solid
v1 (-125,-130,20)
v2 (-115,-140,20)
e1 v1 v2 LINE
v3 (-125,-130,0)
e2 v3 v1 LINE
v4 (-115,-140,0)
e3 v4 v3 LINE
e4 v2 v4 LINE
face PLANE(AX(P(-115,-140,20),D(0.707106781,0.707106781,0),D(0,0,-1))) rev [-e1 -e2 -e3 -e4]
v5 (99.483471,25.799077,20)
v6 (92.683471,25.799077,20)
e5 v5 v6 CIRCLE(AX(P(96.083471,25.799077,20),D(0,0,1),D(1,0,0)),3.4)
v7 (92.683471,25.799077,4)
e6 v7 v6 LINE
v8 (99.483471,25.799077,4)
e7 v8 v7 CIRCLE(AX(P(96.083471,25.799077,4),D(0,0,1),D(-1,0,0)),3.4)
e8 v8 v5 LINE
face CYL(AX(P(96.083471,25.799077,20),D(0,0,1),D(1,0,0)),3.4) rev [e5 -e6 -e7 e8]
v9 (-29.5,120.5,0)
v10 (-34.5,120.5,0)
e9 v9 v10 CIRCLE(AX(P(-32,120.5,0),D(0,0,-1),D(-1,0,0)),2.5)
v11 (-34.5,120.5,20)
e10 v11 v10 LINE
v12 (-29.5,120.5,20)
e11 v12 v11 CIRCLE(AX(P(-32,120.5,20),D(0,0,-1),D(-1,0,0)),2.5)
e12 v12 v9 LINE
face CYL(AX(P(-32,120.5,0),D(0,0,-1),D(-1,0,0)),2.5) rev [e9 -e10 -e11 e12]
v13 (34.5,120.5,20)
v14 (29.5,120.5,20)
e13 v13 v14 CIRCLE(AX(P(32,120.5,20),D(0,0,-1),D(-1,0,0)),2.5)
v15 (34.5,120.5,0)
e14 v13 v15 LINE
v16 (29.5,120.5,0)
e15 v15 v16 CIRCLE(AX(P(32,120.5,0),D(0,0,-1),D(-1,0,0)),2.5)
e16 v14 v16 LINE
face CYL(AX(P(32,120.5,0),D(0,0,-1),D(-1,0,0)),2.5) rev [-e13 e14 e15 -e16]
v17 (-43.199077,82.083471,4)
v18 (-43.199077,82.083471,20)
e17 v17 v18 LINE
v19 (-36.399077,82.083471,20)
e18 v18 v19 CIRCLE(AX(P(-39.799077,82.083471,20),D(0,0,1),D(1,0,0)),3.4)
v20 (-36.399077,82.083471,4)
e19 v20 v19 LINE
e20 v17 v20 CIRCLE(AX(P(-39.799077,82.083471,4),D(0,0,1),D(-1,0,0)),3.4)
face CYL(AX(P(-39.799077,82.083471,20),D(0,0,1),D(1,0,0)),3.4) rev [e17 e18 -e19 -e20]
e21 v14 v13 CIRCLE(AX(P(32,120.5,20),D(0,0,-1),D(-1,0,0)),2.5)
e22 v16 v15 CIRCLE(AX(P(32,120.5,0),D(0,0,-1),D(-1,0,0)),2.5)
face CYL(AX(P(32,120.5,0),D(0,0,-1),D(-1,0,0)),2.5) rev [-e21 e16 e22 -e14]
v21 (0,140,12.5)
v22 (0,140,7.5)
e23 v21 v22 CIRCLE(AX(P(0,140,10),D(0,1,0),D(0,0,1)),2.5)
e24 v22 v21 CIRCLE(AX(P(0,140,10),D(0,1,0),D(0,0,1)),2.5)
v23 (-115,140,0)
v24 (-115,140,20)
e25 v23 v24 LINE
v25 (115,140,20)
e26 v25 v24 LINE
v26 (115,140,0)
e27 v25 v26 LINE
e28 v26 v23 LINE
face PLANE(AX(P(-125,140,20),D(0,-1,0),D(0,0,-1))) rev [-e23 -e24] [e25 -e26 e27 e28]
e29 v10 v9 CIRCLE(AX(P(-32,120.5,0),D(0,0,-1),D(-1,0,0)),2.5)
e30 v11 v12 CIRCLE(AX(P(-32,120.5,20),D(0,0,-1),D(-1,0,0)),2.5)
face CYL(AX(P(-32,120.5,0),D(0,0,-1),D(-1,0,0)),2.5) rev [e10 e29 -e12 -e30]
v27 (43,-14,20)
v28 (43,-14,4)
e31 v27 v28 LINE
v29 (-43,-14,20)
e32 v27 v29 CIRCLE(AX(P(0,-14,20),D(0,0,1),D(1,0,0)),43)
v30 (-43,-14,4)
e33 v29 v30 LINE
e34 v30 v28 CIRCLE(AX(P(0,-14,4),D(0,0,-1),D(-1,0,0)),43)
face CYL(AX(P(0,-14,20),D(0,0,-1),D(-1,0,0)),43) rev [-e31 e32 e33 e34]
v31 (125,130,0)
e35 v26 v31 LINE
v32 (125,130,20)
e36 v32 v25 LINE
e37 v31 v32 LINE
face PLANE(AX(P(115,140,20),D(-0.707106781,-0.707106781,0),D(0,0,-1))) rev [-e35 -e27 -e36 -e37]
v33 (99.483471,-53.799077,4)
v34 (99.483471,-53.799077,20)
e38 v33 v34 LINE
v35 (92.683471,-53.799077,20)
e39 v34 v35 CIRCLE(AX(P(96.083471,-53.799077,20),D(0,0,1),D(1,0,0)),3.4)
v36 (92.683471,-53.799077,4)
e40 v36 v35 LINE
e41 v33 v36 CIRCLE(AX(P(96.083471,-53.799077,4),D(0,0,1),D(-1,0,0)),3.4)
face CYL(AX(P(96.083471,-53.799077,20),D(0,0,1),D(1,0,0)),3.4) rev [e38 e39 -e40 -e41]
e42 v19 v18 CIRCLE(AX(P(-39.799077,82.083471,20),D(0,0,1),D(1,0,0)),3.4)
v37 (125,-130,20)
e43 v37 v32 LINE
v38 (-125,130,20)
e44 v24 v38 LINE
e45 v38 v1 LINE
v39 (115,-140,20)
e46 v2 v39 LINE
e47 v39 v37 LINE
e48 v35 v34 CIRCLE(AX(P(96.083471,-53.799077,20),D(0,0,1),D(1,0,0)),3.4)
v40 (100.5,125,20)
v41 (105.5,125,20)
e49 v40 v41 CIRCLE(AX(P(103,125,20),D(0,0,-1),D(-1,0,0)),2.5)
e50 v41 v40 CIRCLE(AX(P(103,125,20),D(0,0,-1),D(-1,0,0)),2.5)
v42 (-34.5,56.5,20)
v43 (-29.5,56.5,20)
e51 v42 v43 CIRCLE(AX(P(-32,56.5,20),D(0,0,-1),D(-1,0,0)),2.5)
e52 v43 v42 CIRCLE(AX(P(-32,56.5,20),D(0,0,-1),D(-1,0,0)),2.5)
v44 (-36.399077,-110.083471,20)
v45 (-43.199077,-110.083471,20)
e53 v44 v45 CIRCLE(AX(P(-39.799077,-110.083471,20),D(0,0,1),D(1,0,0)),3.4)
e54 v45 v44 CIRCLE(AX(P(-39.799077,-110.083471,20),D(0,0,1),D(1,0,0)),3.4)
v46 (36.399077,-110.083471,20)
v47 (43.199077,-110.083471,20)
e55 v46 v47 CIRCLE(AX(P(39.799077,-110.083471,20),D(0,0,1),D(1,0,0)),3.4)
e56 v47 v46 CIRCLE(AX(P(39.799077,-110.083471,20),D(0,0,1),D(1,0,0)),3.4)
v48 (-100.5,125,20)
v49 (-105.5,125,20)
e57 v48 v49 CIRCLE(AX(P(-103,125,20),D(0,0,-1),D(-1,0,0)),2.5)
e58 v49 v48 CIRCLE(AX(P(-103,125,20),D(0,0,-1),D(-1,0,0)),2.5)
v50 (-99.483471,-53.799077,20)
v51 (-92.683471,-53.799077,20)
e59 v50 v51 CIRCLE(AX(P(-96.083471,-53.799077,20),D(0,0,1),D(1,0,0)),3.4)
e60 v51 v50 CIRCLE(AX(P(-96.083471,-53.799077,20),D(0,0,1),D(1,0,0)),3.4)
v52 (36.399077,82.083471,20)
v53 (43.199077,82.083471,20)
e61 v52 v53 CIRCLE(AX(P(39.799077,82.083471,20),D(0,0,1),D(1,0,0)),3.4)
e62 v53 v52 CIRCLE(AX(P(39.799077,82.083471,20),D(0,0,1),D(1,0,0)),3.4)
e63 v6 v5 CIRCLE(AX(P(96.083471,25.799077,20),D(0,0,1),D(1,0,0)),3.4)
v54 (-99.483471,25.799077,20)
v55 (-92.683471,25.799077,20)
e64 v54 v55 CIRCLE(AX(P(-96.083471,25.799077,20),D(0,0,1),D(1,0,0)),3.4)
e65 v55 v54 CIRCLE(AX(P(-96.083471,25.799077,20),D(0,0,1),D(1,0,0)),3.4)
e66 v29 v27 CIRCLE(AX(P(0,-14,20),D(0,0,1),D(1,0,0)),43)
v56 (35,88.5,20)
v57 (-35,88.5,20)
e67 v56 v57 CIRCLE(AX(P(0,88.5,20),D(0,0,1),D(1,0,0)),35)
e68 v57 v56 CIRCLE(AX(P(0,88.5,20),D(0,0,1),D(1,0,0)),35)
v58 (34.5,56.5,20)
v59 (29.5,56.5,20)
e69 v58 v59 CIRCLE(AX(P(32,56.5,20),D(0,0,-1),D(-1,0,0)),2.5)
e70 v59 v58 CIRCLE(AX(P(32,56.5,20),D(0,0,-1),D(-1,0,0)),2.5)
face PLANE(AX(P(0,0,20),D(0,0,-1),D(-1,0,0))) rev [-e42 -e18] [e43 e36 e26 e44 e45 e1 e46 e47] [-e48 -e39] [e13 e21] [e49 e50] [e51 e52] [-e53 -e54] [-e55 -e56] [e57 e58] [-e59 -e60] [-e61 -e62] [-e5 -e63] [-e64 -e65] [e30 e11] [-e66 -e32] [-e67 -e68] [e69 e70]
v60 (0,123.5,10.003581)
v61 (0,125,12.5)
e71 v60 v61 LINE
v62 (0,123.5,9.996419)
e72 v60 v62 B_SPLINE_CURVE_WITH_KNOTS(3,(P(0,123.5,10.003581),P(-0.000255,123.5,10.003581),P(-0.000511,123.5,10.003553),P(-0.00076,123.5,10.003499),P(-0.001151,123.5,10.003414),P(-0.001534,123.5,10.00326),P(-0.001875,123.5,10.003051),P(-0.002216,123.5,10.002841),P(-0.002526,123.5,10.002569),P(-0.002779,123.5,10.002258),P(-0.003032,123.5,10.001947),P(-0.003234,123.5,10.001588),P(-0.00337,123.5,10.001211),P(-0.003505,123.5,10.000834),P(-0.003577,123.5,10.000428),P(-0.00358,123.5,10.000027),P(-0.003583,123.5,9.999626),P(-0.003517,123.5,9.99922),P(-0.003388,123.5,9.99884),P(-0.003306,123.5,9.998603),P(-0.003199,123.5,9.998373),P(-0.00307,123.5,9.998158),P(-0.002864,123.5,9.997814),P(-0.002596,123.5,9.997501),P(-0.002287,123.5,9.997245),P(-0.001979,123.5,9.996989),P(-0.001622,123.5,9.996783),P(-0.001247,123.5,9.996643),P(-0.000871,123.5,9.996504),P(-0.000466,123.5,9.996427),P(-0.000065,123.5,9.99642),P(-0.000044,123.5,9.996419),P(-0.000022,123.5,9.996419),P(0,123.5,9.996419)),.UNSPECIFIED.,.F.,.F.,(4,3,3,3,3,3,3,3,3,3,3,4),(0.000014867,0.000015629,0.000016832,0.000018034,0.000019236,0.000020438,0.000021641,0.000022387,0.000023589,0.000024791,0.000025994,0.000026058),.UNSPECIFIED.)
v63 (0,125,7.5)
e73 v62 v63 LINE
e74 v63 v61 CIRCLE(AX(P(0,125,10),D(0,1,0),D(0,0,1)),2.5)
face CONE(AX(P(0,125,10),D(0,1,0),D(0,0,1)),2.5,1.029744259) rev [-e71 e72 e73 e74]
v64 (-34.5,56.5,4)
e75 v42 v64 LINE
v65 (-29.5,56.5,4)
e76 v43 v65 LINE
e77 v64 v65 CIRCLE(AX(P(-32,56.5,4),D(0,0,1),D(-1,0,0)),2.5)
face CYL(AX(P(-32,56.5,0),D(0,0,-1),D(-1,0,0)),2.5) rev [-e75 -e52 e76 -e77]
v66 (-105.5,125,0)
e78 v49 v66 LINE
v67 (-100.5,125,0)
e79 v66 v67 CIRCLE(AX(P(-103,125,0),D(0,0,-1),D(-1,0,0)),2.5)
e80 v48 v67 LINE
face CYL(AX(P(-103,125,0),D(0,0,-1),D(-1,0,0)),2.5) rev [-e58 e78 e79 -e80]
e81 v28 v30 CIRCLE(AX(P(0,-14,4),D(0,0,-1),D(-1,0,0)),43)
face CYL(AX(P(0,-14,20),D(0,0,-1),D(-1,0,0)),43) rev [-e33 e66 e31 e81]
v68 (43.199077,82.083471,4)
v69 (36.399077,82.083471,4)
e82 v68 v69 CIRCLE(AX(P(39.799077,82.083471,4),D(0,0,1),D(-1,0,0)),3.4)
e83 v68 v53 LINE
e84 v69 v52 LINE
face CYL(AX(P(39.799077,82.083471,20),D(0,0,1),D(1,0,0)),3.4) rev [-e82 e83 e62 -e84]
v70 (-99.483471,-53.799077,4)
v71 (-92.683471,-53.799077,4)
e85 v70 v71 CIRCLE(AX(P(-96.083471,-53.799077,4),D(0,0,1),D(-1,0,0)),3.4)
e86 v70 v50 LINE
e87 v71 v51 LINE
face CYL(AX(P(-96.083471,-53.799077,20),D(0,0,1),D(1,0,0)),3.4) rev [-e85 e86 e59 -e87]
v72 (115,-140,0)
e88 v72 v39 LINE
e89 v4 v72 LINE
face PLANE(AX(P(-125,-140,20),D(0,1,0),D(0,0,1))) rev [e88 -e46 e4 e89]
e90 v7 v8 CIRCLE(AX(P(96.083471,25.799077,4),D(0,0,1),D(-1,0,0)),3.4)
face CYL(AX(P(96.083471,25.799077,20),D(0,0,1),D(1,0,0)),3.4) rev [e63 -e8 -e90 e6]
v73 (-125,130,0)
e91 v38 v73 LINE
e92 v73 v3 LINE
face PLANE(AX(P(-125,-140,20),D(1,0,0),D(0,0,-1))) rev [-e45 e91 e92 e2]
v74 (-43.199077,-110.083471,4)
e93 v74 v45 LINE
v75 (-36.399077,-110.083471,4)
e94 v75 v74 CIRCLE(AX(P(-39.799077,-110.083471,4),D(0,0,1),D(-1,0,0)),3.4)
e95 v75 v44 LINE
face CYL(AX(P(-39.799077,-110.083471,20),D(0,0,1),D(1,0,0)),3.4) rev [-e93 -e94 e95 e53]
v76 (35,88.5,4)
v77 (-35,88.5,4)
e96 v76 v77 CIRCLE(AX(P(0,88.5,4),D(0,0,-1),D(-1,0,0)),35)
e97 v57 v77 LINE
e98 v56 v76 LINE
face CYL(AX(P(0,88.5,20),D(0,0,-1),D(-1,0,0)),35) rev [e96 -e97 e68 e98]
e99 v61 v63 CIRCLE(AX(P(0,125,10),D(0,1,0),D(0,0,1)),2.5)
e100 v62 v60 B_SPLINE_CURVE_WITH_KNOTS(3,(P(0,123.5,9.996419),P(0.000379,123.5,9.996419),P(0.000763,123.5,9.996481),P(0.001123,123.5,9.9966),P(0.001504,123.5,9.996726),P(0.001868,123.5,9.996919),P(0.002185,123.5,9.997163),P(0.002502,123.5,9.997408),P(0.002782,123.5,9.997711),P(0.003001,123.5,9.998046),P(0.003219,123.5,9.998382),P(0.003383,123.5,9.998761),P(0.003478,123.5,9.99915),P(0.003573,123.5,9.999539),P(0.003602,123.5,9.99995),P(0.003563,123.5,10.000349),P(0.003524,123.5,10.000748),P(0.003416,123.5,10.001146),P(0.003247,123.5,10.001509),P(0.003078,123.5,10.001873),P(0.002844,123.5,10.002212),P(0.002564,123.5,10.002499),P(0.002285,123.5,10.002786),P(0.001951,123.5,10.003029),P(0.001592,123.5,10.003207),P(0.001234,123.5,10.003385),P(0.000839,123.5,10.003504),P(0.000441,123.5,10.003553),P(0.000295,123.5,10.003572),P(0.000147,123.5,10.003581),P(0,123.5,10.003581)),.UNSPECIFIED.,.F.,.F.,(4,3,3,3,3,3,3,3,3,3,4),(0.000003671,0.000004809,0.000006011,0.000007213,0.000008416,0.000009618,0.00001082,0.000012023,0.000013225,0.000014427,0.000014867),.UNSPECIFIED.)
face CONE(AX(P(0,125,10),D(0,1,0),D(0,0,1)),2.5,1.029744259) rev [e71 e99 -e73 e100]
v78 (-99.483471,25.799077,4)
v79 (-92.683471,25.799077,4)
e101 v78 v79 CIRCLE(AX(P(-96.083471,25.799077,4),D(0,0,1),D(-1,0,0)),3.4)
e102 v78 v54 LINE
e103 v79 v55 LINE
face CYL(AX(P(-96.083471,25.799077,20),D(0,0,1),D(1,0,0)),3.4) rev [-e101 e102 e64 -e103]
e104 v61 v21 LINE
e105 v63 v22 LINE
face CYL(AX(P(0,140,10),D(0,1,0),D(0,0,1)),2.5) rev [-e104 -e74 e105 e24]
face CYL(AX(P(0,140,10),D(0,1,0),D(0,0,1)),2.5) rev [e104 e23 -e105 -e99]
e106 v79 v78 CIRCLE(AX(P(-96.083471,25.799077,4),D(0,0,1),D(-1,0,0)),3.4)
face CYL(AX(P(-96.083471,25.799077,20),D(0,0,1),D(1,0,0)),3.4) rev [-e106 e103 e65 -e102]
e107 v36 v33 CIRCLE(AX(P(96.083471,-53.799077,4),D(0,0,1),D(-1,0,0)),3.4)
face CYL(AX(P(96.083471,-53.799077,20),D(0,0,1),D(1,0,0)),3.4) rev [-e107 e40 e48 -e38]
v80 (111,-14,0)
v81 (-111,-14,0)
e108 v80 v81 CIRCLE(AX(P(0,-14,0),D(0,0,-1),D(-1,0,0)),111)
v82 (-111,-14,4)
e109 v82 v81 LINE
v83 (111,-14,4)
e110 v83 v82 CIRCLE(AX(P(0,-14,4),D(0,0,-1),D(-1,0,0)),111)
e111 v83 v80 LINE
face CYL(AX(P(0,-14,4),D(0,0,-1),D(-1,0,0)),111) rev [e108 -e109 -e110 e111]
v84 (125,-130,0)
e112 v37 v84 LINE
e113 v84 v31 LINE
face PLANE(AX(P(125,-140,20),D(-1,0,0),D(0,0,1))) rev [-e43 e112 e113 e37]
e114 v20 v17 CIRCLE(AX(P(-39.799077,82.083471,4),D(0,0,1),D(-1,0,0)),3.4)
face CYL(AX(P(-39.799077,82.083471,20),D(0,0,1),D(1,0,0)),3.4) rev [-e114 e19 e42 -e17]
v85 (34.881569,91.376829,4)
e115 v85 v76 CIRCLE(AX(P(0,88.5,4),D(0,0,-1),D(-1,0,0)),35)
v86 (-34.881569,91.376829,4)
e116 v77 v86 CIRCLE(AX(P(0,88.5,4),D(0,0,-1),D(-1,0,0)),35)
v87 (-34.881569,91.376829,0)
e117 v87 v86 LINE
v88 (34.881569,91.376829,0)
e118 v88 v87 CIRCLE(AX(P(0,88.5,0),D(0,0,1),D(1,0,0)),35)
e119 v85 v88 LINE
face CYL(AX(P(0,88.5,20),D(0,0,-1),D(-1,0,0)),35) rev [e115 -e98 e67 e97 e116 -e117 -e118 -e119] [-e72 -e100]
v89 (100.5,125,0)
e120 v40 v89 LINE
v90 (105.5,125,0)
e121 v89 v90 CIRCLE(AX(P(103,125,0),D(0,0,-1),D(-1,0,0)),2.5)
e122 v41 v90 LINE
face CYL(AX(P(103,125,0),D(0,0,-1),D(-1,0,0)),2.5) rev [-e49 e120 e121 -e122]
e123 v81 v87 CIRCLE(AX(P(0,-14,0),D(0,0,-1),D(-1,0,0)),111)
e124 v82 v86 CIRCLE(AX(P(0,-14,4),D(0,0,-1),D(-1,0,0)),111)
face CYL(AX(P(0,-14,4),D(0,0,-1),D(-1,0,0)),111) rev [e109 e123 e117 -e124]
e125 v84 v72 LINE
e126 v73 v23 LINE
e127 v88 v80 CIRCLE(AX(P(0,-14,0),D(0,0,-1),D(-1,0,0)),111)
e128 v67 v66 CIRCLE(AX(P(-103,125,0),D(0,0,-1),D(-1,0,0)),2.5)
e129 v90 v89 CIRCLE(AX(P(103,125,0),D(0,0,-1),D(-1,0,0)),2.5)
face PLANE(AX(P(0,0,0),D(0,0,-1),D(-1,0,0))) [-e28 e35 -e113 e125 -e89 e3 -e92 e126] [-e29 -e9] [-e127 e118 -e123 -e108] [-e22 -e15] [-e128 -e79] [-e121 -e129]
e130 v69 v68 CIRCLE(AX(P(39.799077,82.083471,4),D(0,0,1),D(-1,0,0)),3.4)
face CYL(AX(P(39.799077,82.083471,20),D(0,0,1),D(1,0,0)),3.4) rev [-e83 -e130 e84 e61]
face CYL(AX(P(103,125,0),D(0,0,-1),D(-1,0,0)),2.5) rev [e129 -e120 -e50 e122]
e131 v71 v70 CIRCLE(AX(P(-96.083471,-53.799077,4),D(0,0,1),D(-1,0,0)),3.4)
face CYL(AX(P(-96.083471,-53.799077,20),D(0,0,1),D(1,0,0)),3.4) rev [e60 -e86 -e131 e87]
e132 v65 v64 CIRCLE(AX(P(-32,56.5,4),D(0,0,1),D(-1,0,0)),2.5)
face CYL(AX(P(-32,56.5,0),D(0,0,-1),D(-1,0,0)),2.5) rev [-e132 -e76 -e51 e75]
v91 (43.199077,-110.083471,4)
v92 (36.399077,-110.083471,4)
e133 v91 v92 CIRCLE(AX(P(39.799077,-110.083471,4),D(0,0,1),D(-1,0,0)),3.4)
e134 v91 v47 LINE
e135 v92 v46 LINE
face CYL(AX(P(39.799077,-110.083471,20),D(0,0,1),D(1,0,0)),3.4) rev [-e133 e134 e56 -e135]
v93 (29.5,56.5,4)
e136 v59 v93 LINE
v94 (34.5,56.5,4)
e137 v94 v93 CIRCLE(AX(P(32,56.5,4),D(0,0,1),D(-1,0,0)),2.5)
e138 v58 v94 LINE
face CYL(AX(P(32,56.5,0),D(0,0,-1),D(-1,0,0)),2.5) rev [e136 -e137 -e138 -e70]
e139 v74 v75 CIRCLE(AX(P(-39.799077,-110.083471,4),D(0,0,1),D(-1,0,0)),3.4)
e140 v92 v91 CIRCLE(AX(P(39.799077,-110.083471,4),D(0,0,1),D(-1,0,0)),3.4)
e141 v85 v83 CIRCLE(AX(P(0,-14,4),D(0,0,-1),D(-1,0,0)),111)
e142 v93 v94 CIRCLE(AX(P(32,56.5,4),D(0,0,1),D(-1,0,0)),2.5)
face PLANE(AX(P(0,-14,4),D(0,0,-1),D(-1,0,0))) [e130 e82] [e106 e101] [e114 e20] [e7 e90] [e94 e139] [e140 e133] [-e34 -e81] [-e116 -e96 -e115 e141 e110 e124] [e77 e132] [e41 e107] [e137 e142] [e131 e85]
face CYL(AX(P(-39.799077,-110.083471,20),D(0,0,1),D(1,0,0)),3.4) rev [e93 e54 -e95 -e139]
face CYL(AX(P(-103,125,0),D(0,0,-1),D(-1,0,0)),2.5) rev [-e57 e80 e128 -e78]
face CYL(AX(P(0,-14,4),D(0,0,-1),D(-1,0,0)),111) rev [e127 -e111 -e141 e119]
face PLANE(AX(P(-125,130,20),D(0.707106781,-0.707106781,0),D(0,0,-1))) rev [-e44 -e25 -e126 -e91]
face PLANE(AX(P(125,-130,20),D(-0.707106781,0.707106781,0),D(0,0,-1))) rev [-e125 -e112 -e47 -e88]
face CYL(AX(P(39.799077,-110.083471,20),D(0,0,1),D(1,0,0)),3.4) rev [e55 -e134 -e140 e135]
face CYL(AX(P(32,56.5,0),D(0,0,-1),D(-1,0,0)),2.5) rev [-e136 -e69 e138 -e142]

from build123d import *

# Parameters (mm, degrees)
SKETCH_1_W             = 250
SKETCH_1_H             = 280
SKETCH_1_R             = 43
SKETCH_1_R_2           = 35
EXTRUDE_1_DEPTH        = 20
HOLE_WIZARD_M8_1_D     = 6.8
HOLE_WIZARD_M6_1_D     = 5
SKETCH_6_R             = 111
CUT_EXTRUDE_1_DEPTH    = 4
CHAMFER_1_SIZE         = 10
HOLE_WIZARD_M6_2_D     = 5
HOLE_WIZARD_M6_3_D     = 5
HOLE_WIZARD_M6_3_DEPTH = 15
HOLE_WIZARD_M6_3_TIP   = 1.502151548


with BuildPart() as part:
    # 草图1 → 凸台-拉伸1 (new body)
    with BuildSketch(Plane.XY):
        Rectangle(SKETCH_1_W, SKETCH_1_H)
        with Locations((0, -14)):
            Circle(SKETCH_1_R, mode=Mode.SUBTRACT)
        with Locations((0, 88.5)):
            Circle(SKETCH_1_R_2, mode=Mode.SUBTRACT)
    extrude(amount=EXTRUDE_1_DEPTH)

    # M8 螺纹孔1 (through all)
    with Locations(Plane.XY.offset(20)):
        with Locations((-39.799076966, 82.083471381), (39.799076966, 82.083471381), (96.083471381, 25.799076966), (96.083471381, -53.799076966), (39.799076966, -110.083471381), (-39.799076966, -110.083471381), (-96.083471381, -53.799076966), (-96.083471381, 25.799076966)):
            Hole(HOLE_WIZARD_M8_1_D / 2)

    # M6 螺纹孔1 (through all)
    with Locations(Plane(origin=(0, 0, 0), x_dir=(-1, 0, 0), z_dir=(0, 0, -1))):
        with Locations((0, 88.5), (32, 120.5), (-32, 56.5), (-32, 120.5), (32, 56.5)):
            Hole(HOLE_WIZARD_M6_1_D / 2)

    # 草图6 → 切除-拉伸1 (cut)
    with BuildSketch(Plane(origin=(0, 0, 0), x_dir=(-1, 0, 0), z_dir=(0, 0, -1))):
        with Locations((0, -14)):
            Circle(SKETCH_6_R)
    extrude(amount=-CUT_EXTRUDE_1_DEPTH, mode=Mode.SUBTRACT)

    # 倒角1
    chamfer_1_edges = [part.edges().sort_by_distance(p)[0] for p in [
        (125, -140, 10),
        (-125, -140, 10),
        (-125, 140, 10),
        (125, 140, 10),
    ]]
    chamfer(chamfer_1_edges, length=CHAMFER_1_SIZE)

    # M6 螺纹孔2 (through all)
    with Locations(Plane(origin=(0, 0, 0), x_dir=(-1, 0, 0), z_dir=(0, 0, -1))):
        with Locations((103, 125), (-103, 125)):
            Hole(HOLE_WIZARD_M6_2_D / 2)

    # M6 螺纹孔3
    with Locations(Plane(origin=(0, 140, 0), x_dir=(1, 0, 0), z_dir=(0, 1, 0))):
        with Locations((0, -10)):
            Hole(HOLE_WIZARD_M6_3_D / 2, depth=HOLE_WIZARD_M6_3_DEPTH)
            with Locations((0, 0, -(HOLE_WIZARD_M6_3_DEPTH + HOLE_WIZARD_M6_3_TIP / 2))):  # 118° drill point
                Cone(0, HOLE_WIZARD_M6_3_D / 2, HOLE_WIZARD_M6_3_TIP, mode=Mode.SUBTRACT)


solid = part.part
